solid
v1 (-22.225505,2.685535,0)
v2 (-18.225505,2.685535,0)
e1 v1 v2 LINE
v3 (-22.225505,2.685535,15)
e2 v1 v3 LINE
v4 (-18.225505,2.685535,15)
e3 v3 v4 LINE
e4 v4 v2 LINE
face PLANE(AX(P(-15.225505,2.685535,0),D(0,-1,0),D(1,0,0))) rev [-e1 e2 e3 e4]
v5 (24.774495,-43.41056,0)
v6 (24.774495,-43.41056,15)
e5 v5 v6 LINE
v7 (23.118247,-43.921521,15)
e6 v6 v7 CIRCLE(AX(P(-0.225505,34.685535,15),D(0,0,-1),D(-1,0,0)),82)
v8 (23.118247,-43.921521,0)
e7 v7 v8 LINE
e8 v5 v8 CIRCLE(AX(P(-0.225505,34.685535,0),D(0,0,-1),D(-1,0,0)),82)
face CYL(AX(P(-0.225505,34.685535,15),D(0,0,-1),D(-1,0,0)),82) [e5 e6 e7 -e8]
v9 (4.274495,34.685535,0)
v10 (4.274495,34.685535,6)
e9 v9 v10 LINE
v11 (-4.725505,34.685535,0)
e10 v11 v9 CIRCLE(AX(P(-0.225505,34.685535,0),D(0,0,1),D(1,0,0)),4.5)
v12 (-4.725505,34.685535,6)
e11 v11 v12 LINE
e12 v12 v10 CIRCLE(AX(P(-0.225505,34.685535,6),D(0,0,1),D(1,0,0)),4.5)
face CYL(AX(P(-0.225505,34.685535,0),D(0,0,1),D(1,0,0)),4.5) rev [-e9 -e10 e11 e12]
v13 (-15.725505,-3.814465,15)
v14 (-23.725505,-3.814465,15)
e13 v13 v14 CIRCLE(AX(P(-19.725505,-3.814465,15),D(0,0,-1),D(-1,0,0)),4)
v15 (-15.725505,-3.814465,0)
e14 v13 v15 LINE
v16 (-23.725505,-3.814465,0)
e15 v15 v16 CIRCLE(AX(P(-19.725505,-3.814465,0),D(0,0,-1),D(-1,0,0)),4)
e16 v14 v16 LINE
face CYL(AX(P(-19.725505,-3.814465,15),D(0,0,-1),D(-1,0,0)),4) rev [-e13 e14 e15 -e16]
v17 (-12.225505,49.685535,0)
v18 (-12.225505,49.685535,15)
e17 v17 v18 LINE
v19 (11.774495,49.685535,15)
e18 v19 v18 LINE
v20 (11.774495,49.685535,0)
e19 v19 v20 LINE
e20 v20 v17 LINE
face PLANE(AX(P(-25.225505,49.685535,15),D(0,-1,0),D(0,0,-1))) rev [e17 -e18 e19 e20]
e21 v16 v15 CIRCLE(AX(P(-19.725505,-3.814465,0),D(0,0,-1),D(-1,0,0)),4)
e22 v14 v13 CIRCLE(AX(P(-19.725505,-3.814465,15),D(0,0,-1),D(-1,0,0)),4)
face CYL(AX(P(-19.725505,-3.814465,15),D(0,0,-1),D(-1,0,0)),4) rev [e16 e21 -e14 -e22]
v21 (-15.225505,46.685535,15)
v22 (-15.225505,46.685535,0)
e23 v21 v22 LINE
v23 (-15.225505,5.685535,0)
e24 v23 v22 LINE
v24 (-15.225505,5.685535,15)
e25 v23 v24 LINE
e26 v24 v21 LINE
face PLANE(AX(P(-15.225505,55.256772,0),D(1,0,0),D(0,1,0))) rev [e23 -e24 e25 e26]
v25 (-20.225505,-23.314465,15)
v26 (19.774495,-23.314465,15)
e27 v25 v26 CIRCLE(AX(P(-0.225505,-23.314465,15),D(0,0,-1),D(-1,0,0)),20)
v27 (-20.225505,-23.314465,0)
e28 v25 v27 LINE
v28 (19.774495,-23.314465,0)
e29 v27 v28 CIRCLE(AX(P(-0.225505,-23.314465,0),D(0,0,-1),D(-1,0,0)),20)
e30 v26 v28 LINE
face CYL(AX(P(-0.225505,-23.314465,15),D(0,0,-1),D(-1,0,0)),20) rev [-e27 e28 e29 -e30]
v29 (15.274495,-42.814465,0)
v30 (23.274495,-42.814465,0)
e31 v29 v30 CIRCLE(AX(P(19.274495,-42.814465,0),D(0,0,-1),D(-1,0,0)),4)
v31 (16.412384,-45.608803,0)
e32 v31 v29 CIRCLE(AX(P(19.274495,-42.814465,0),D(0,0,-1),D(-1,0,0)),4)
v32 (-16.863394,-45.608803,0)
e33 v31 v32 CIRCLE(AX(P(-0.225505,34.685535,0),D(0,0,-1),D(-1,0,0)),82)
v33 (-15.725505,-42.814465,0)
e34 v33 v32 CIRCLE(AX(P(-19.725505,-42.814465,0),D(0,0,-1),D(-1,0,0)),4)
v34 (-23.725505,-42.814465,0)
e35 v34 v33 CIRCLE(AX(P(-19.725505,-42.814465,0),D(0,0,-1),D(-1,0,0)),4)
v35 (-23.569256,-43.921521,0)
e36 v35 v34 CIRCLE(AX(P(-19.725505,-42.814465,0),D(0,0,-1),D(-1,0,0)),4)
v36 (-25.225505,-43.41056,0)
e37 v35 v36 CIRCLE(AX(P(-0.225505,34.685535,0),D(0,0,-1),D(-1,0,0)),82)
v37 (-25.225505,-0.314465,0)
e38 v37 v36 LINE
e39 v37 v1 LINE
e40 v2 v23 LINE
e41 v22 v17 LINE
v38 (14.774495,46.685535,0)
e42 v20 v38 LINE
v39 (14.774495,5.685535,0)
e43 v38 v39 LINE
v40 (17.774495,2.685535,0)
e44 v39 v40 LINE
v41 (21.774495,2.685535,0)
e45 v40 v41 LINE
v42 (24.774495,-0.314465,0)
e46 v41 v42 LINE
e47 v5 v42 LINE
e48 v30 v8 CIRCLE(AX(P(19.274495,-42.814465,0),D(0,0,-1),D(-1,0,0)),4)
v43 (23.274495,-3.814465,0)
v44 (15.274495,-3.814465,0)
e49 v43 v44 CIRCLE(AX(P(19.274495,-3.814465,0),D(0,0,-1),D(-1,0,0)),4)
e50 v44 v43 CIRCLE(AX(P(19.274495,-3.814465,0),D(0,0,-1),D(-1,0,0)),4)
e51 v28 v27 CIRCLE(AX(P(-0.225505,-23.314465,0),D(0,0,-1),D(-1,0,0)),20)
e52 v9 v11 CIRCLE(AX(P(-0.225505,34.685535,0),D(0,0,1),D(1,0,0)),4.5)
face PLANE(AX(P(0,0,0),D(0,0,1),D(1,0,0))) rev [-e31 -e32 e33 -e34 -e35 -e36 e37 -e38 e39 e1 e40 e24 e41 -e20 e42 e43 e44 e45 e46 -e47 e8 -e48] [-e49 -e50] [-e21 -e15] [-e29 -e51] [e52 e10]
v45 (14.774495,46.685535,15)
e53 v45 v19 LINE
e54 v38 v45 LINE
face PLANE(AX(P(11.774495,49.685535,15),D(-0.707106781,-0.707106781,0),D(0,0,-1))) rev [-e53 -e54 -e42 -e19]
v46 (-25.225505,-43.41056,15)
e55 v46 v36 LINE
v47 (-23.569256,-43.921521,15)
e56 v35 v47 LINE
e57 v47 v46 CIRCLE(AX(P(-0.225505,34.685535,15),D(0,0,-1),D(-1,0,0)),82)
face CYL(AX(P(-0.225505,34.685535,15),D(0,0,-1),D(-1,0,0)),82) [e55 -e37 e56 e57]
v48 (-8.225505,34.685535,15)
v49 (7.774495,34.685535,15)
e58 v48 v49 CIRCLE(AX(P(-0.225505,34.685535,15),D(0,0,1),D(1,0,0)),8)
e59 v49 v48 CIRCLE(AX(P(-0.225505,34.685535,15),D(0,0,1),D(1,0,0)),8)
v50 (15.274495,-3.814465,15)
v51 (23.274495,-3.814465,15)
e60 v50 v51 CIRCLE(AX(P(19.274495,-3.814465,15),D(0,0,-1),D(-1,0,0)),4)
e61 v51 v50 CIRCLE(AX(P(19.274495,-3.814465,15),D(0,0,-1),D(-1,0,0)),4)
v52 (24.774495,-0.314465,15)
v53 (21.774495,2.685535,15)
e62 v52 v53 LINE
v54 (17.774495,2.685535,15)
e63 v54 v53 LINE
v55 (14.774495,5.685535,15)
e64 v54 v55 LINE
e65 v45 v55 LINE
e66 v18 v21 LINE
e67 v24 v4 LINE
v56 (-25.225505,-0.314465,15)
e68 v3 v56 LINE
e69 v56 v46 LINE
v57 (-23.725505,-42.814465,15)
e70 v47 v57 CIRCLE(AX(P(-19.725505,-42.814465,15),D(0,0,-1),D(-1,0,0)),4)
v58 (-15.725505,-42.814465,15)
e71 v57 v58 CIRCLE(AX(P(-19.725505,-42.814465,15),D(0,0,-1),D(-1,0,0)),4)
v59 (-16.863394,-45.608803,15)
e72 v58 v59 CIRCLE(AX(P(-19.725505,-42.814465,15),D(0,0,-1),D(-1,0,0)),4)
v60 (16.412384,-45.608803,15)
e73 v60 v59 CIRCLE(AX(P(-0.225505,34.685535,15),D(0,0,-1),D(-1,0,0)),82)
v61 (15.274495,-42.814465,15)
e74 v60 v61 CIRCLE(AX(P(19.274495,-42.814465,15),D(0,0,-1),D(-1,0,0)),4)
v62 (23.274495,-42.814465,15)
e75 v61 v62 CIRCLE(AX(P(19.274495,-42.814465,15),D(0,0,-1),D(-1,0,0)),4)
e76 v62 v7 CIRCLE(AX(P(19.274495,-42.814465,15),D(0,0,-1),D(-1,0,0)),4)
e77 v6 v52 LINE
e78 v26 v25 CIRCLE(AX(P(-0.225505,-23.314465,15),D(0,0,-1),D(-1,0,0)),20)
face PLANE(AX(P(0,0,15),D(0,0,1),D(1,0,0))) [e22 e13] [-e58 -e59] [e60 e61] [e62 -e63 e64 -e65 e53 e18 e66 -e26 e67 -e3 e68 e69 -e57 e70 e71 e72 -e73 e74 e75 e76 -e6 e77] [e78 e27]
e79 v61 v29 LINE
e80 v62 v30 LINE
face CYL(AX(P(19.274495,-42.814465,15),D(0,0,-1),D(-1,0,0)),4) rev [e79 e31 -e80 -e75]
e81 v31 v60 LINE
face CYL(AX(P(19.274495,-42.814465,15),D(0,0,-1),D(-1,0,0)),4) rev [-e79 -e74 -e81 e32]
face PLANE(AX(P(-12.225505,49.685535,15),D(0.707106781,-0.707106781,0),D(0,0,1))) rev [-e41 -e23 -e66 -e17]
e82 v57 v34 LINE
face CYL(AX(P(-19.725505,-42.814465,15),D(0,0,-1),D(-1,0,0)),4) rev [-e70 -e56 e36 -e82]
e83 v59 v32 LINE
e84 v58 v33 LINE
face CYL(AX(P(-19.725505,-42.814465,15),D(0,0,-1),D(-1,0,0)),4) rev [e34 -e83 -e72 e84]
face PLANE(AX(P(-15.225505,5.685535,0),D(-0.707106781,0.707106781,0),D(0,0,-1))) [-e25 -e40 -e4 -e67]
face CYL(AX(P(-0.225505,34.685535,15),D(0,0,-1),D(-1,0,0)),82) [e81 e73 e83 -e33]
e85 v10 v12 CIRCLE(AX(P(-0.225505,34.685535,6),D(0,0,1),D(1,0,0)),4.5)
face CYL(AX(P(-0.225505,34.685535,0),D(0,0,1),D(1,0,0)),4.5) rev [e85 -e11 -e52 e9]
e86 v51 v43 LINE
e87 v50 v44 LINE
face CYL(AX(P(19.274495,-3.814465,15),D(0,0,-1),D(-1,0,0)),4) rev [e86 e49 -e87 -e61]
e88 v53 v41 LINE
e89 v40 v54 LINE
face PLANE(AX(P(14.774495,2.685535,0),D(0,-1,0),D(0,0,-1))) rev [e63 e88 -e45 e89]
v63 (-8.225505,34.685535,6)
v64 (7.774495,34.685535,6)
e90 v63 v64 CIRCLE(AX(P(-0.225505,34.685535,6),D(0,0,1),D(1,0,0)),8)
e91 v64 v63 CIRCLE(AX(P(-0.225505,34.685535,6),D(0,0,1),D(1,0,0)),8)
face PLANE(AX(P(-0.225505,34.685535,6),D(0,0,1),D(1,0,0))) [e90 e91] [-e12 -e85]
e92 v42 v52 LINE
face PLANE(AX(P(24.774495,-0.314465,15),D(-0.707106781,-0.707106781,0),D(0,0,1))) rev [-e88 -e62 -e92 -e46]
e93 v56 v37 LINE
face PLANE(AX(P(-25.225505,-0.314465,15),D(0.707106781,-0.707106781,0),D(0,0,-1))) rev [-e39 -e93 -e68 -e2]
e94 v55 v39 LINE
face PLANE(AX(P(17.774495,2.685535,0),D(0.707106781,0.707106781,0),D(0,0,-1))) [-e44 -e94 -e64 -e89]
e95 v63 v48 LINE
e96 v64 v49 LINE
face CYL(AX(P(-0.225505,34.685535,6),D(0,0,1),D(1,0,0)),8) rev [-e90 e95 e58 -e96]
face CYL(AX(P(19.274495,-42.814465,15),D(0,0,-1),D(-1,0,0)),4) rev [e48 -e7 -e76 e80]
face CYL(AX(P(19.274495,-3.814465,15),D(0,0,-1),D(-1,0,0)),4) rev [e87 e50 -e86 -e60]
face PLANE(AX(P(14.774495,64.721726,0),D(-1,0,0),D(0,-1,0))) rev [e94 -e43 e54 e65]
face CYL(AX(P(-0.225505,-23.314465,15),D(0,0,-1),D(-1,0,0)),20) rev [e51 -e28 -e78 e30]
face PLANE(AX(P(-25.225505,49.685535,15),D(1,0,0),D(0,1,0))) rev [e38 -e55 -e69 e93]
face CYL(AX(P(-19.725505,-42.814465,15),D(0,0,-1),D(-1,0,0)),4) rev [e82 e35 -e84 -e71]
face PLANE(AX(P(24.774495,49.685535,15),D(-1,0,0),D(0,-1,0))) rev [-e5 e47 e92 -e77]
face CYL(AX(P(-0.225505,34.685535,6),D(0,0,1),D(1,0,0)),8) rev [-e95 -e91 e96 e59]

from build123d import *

# Parameters (mm, degrees)
SKETCH1_W           = 50
SKETCH1_H           = 97
BOSS_EXTRUDE1_DEPTH = 15
SKETCH6_R           = 8
CUT_EXTRUDE3_DEPTH  = 9
SKETCH7_R           = 4.5
CUT_EXTRUDE4_DEPTH  = 57.444472183
SKETCH8_R           = 20
SKETCH8_R_2         = 4
CUT_EXTRUDE5_DEPTH  = 58.705965376
SKETCH9_W           = 32.009633737
SKETCH9_H           = 62.03619176
SKETCH9_W_2         = 30.458131691
SKETCH9_H_2         = 52.571237354
CUT_EXTRUDE6_DEPTH  = 58.705965376
CHAMFER1_SIZE       = 3
SKETCH14_R          = 119.720313389
SKETCH14_R_2        = 82
CUT_EXTRUDE10_DEPTH = 58.705965376


with BuildPart() as part:
    # Sketch1 → Boss-Extrude1 (new body)
    with BuildSketch(Plane.XY):
        with Locations((-0.2255048, 1.185534591)):
            Rectangle(SKETCH1_W, SKETCH1_H)
    extrude(amount=BOSS_EXTRUDE1_DEPTH)

    # Sketch6 → Cut-Extrude3 (cut)
    with BuildSketch(Plane.XY.offset(15)):
        with Locations((-0.2255048, 34.685534591)):
            Circle(SKETCH6_R)
    extrude(amount=-CUT_EXTRUDE3_DEPTH, mode=Mode.SUBTRACT)

    # Sketch7 → Cut-Extrude4 (cut, through all)
    with BuildSketch(Plane.XY.offset(6)):
        with Locations((-0.2255048, 34.685534591)):
            Circle(SKETCH7_R)
    extrude(amount=-CUT_EXTRUDE4_DEPTH, mode=Mode.SUBTRACT)

    # Sketch8 → Cut-Extrude5 (cut, through all)
    with BuildSketch(Plane(origin=(0, 0, 0), x_dir=(-1, 0, 0), z_dir=(0, 0, -1))):
        with Locations((0.2255048, -23.314465409)):
            Circle(SKETCH8_R)
        with Locations((-19.2744952, -42.814465409)):
            Circle(SKETCH8_R_2)
        with Locations((-19.2744952, -3.814465409)):
            Circle(SKETCH8_R_2)
        with Locations((19.7255048, -3.814465409)):
            Circle(SKETCH8_R_2)
        with Locations((19.7255048, -42.814465409)):
            Circle(SKETCH8_R_2)
    extrude(amount=-CUT_EXTRUDE5_DEPTH, mode=Mode.SUBTRACT)

    # Sketch9 → Cut-Extrude6 (cut, through all)
    with BuildSketch(Plane.XY.offset(15)):
        with Locations((30.779312069, 33.703630471)):
            Rectangle(SKETCH9_W, SKETCH9_H)
        with Locations((-30.454570646, 28.971153268)):
            Rectangle(SKETCH9_W_2, SKETCH9_H_2)
    extrude(amount=-CUT_EXTRUDE6_DEPTH, mode=Mode.SUBTRACT)

    # Chamfer1
    chamfer1_edges = [part.edges().sort_by_distance(p)[0] for p in [
        (14.7744952, 49.685534591, 7.5),
        (14.7744952, 2.685534591, 7.5),
        (24.7744952, 2.685534591, 7.5),
        (-15.2255048, 49.685534591, 7.5),
        (-25.2255048, 2.685534591, 7.5),
        (-15.2255048, 2.685534591, 7.5),
    ]]
    chamfer(chamfer1_edges, length=CHAMFER1_SIZE)

    # Sketch14 → Cut-Extrude10 (cut, through all)
    with BuildSketch(Plane(origin=(0, 0, 0), x_dir=(-1, 0, 0), z_dir=(0, 0, -1))):
        with Locations((0.2255048, 34.685534591)):
            Circle(SKETCH14_R)
        with Locations((0.2255048, 34.685534591)):
            Circle(SKETCH14_R_2, mode=Mode.SUBTRACT)
    extrude(amount=-CUT_EXTRUDE10_DEPTH, mode=Mode.SUBTRACT)


solid = part.part
